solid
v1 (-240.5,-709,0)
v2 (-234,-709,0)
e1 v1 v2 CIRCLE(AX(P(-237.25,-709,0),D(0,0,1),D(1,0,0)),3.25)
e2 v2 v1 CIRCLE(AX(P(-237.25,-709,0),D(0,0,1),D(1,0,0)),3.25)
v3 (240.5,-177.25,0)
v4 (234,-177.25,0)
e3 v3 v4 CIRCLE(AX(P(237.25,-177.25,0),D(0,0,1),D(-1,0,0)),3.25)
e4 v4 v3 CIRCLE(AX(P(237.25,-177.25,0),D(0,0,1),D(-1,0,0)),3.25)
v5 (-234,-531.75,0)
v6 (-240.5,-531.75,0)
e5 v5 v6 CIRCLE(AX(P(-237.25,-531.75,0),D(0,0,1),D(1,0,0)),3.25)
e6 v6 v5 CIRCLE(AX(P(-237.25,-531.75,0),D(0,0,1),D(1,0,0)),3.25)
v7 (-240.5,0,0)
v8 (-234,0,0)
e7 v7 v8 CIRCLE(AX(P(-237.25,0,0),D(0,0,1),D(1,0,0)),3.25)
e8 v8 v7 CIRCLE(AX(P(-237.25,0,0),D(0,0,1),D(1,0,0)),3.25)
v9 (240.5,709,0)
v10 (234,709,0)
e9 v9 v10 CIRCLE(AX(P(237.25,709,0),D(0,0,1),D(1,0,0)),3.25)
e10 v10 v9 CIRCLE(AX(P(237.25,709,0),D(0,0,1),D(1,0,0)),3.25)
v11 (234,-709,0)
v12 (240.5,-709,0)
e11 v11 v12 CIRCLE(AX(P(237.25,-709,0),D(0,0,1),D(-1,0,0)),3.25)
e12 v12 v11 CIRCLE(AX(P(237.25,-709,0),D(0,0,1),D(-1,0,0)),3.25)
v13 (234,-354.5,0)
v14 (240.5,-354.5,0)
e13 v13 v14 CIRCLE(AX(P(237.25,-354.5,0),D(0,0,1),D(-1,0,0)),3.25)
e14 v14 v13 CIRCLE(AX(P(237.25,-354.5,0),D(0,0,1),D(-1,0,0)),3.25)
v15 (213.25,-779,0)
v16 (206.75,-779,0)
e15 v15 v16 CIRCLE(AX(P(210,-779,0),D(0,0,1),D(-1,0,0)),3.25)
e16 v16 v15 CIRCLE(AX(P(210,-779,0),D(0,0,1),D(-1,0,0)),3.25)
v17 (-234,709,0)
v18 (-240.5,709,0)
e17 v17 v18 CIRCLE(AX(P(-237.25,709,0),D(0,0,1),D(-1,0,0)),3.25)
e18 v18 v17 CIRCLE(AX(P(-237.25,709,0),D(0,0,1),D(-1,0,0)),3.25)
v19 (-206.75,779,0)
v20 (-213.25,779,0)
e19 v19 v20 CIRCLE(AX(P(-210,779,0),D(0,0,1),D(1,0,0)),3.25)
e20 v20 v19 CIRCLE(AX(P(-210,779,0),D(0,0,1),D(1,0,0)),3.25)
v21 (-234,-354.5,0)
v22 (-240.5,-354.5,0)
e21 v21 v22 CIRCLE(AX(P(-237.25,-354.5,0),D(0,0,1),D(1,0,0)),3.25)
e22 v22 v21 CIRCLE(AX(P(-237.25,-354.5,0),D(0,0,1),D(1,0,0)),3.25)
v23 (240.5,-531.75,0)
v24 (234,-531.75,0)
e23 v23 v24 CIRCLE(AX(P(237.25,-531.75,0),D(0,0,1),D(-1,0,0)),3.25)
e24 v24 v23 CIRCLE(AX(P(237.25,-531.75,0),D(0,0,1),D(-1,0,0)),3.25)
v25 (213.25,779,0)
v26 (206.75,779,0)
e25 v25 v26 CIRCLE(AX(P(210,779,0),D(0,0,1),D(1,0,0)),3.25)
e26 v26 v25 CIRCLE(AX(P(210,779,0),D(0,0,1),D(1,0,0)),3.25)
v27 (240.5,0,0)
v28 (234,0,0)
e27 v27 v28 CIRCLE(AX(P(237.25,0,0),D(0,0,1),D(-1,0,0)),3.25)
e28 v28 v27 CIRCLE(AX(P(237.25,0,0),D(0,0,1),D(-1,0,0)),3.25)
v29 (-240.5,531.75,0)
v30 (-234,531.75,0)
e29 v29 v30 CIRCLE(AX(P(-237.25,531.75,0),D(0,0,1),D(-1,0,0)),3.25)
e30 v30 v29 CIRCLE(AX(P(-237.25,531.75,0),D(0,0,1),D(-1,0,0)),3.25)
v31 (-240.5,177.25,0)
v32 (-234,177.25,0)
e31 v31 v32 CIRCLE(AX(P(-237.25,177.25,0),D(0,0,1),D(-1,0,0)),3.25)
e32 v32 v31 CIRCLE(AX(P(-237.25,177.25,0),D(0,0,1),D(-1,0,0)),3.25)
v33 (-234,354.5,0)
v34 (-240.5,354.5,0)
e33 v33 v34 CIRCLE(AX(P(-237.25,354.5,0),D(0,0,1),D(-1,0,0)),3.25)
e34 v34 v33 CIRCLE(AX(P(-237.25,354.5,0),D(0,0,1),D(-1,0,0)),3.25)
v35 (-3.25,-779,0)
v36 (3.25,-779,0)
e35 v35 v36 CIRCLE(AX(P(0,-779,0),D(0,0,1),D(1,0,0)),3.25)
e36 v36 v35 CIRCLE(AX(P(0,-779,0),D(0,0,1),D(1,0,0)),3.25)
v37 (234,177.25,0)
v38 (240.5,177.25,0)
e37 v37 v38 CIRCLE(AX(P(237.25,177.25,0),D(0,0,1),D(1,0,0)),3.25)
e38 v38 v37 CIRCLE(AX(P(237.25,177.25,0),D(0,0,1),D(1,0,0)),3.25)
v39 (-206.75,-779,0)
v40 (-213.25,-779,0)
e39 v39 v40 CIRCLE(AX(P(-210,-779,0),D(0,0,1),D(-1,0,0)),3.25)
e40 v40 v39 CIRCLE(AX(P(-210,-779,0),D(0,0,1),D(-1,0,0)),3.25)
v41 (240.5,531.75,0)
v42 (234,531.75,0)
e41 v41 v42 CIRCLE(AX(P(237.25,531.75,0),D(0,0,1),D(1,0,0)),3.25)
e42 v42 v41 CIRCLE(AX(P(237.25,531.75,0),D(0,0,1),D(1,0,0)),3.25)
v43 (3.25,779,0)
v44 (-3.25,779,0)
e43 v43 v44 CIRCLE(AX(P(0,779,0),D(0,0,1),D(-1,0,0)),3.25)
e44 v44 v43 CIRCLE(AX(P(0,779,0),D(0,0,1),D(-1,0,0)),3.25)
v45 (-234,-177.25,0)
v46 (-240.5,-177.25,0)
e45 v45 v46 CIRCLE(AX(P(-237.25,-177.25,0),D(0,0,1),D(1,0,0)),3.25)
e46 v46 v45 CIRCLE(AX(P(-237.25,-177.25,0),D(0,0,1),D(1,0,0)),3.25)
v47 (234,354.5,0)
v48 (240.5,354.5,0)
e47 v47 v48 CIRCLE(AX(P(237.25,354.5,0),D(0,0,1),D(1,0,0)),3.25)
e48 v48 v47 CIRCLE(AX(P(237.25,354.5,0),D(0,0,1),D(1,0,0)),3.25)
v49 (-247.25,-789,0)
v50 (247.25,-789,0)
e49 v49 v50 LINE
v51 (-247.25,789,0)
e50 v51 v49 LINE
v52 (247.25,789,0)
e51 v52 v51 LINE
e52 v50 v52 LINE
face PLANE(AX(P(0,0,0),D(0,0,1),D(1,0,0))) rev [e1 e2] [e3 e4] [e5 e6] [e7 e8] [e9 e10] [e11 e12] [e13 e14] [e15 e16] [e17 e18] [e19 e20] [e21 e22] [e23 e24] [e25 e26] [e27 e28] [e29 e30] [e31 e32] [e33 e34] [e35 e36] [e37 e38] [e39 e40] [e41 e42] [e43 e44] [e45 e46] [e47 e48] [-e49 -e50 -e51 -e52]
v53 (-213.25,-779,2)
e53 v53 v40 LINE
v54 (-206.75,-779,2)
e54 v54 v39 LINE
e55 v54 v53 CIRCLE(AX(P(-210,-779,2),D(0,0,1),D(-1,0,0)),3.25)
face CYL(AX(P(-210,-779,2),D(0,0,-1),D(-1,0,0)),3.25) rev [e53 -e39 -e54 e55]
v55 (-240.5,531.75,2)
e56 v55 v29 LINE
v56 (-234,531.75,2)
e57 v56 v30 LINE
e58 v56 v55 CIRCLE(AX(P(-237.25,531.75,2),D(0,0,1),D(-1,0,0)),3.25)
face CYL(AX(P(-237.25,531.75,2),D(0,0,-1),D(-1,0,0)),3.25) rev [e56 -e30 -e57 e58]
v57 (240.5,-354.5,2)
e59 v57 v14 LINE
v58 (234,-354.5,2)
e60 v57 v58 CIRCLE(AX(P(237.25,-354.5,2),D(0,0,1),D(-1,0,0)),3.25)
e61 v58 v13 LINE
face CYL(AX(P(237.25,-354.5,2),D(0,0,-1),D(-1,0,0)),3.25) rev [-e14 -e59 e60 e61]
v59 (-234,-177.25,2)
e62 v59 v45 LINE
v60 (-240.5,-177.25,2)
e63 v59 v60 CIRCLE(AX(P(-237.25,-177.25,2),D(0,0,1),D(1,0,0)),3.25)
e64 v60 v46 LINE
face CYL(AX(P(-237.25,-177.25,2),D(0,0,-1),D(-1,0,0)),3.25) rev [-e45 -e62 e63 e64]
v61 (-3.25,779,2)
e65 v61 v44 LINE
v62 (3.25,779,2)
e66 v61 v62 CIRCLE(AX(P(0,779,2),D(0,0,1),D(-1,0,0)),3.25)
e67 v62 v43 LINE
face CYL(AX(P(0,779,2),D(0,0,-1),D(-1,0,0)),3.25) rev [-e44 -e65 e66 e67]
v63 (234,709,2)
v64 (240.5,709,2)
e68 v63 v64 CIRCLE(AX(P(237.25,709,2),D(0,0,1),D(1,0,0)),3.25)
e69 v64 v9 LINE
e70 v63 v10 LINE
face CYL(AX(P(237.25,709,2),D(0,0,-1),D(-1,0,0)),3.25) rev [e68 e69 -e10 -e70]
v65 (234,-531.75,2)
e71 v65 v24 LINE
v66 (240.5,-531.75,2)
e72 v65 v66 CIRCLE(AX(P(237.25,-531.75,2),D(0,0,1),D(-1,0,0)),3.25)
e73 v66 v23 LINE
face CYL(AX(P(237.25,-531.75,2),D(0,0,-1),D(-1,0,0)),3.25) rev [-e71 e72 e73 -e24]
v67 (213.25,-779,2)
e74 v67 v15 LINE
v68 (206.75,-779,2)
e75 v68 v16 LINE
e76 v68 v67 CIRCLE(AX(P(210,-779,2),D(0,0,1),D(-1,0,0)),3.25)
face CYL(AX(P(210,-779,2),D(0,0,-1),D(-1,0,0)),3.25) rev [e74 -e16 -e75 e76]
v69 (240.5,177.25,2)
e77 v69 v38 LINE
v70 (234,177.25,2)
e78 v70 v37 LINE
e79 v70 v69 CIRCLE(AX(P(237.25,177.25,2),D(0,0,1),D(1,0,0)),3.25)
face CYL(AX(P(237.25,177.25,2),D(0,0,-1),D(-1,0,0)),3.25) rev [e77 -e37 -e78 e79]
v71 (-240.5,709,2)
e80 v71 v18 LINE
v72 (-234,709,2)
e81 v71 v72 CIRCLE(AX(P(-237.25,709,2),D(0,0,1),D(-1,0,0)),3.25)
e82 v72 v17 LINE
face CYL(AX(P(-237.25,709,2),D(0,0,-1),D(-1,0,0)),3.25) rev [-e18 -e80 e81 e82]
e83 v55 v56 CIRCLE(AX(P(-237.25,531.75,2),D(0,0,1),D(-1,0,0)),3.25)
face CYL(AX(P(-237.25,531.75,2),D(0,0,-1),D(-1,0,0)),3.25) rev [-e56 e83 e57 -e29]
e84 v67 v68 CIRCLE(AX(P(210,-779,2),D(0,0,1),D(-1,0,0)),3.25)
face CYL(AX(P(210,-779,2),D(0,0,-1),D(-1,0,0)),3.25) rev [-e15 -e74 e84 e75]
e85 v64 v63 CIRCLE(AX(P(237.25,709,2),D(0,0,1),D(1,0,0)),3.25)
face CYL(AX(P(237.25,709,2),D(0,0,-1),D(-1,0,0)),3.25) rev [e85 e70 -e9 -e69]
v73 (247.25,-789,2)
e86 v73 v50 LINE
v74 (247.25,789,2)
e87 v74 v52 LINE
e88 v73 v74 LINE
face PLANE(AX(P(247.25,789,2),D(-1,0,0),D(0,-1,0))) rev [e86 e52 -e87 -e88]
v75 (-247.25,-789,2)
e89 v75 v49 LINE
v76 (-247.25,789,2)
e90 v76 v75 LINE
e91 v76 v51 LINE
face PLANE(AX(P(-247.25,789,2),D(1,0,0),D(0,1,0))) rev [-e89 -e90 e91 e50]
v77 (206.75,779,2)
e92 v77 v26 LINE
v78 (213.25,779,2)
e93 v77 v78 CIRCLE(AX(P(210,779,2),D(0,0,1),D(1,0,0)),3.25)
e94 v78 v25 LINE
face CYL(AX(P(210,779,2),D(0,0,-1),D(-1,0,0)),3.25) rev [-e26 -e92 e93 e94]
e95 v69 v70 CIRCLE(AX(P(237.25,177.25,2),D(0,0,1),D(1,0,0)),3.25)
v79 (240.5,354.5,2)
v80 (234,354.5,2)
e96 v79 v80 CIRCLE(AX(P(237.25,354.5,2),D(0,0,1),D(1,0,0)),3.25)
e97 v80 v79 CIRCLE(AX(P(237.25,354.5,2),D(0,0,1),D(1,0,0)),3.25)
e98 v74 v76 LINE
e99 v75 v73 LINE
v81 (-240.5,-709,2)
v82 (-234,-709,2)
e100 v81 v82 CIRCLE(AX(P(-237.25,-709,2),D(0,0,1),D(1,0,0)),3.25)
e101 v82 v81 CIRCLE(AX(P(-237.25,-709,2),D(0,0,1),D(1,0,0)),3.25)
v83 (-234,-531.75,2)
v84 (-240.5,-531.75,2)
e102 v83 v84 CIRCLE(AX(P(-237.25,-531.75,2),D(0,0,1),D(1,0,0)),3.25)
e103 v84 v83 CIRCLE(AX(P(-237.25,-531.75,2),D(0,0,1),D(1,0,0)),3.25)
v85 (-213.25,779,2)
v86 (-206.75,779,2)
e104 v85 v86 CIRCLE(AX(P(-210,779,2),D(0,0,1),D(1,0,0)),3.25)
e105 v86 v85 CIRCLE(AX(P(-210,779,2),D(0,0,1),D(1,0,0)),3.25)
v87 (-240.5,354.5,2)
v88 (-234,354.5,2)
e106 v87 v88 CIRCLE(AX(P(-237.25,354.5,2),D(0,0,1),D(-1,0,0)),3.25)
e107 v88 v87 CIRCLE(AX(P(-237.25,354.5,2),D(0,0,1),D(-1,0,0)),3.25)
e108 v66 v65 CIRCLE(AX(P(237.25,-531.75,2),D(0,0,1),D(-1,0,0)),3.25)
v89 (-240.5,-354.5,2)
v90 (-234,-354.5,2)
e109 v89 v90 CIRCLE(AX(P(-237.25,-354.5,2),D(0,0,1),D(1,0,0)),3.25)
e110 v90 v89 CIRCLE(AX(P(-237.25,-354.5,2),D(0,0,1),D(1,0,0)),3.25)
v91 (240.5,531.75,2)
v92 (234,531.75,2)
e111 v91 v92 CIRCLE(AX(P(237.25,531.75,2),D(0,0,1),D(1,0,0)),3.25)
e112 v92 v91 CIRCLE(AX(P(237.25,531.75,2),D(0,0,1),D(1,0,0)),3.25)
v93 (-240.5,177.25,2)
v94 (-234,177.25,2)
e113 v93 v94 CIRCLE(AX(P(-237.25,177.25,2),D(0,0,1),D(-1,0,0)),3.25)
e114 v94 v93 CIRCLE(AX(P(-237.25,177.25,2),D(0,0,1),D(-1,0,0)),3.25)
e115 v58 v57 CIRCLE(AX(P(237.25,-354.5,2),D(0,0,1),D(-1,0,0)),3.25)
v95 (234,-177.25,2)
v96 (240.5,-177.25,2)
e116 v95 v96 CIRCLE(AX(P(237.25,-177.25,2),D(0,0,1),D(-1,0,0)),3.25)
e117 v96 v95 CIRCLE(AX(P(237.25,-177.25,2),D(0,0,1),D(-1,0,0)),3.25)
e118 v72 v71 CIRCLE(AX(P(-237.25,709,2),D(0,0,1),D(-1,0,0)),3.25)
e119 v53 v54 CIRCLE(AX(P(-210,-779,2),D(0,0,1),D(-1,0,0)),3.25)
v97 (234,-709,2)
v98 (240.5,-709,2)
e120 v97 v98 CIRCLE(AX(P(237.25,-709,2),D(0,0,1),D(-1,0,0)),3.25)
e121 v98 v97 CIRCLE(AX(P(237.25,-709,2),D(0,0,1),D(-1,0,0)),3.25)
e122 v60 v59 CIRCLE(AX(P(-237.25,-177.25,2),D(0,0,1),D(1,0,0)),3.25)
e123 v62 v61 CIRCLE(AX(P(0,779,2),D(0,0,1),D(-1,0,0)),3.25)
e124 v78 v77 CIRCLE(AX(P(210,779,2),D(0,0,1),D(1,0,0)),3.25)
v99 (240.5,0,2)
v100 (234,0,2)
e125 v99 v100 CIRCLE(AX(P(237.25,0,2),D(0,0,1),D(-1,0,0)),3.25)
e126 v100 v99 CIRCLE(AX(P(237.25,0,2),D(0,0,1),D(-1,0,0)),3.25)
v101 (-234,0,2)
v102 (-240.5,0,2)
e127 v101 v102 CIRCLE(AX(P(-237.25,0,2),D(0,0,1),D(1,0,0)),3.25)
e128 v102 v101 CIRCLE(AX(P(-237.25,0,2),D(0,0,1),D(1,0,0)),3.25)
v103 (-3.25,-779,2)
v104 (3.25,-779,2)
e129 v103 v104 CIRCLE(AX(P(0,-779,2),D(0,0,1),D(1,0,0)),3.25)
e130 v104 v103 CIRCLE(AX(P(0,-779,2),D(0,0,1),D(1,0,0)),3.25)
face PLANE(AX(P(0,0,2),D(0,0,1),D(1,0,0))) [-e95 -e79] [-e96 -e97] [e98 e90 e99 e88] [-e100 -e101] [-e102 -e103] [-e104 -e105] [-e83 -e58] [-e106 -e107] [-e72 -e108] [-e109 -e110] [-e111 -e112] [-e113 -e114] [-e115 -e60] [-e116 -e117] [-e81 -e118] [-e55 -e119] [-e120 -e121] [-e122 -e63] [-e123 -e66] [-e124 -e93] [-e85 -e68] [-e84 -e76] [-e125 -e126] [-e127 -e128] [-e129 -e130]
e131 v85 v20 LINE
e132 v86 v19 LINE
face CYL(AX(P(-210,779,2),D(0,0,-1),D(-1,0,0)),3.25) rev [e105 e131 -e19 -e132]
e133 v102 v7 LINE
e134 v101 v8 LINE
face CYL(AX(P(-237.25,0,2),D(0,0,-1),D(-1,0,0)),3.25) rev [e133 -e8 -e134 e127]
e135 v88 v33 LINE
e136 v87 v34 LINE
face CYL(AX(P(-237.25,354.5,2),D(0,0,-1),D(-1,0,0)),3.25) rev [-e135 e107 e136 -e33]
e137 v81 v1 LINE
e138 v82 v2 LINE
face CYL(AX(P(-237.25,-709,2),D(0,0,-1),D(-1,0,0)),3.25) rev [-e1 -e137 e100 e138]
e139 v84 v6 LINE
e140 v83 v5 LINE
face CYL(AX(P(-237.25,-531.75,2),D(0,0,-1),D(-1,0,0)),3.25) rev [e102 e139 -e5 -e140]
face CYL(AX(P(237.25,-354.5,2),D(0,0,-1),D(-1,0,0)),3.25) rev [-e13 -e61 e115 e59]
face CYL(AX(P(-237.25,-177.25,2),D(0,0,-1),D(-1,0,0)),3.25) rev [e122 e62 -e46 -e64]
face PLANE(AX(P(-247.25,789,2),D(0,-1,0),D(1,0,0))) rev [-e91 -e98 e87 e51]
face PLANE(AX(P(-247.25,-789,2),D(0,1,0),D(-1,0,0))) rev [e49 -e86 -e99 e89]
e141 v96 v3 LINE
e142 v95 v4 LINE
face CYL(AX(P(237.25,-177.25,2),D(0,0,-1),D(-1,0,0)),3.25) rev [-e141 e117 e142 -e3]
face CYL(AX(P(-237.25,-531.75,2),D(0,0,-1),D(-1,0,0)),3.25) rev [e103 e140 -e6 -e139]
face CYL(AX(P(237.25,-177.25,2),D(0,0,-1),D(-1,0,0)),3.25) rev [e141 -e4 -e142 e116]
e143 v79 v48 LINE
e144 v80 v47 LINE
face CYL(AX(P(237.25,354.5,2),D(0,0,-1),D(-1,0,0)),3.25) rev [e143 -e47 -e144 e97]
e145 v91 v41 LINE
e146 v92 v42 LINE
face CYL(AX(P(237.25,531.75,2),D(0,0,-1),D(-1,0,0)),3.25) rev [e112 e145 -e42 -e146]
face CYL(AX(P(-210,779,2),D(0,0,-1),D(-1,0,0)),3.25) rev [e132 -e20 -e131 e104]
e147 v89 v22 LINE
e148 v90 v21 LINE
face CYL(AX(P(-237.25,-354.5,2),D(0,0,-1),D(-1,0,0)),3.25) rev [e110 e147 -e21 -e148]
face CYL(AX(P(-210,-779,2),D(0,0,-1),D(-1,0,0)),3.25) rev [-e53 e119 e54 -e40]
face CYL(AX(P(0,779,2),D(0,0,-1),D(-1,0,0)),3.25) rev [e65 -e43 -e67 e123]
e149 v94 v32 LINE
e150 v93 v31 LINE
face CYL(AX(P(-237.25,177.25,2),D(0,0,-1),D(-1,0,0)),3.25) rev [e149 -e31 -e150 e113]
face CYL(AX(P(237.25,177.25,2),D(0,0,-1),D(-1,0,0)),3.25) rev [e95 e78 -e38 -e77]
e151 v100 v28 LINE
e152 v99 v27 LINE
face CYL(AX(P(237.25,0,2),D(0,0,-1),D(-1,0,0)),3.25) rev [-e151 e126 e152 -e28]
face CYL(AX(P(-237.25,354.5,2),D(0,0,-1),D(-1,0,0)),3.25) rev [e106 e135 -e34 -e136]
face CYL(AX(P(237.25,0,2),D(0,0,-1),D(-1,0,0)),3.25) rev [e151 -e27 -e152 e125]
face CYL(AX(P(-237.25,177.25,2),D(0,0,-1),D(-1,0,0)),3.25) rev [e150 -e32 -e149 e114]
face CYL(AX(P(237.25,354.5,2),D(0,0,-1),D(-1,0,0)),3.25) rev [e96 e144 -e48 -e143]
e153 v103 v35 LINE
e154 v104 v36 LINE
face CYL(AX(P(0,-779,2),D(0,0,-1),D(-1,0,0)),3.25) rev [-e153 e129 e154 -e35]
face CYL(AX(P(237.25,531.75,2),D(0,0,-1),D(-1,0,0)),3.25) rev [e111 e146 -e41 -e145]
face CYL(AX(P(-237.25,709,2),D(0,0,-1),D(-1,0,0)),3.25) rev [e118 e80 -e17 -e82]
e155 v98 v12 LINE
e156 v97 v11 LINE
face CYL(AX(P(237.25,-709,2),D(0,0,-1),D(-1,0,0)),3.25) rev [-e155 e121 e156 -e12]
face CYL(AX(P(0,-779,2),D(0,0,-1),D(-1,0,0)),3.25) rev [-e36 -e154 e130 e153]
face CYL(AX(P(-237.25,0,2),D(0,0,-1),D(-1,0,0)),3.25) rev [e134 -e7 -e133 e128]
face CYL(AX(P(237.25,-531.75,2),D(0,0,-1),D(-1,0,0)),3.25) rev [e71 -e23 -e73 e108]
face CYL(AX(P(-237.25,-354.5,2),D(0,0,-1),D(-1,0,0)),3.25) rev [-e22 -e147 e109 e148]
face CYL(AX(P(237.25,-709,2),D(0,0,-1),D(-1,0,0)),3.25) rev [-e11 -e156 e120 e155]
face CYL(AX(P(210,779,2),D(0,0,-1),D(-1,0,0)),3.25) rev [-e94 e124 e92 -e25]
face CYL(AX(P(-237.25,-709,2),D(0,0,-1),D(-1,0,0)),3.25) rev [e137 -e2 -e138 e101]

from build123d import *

# Parameters (mm, degrees)
SKETCH_1_W      = 494.5
SKETCH_1_H      = 1578
SKETCH_1_R      = 3.25
EXTRUDE_1_DEPTH = 2


with BuildPart() as part:
    # 草图1 → 凸台-拉伸1 (new body)
    with BuildSketch(Plane.XY):
        Rectangle(SKETCH_1_W, SKETCH_1_H)
        with Locations((-237.25, 0)):
            Circle(SKETCH_1_R, mode=Mode.SUBTRACT)
        with Locations((-237.25, -177.25)):
            Circle(SKETCH_1_R, mode=Mode.SUBTRACT)
        with Locations((-237.25, -354.5)):
            Circle(SKETCH_1_R, mode=Mode.SUBTRACT)
        with Locations((-237.25, -531.75)):
            Circle(SKETCH_1_R, mode=Mode.SUBTRACT)
        with Locations((-237.25, -709)):
            Circle(SKETCH_1_R, mode=Mode.SUBTRACT)
        with Locations((0, -779)):
            Circle(SKETCH_1_R, mode=Mode.SUBTRACT)
        with Locations(Location((0, 779, 0), (0, 0, 180))):
            Circle(SKETCH_1_R, mode=Mode.SUBTRACT)
        with Locations(Location((-237.25, 709, 0), (0, 0, 180))):
            Circle(SKETCH_1_R, mode=Mode.SUBTRACT)
        with Locations(Location((-237.25, 531.75, 0), (0, 0, 180))):
            Circle(SKETCH_1_R, mode=Mode.SUBTRACT)
        with Locations(Location((-237.25, 354.5, 0), (0, 0, 180))):
            Circle(SKETCH_1_R, mode=Mode.SUBTRACT)
        with Locations(Location((-237.25, 177.25, 0), (0, 0, 180))):
            Circle(SKETCH_1_R, mode=Mode.SUBTRACT)
        with Locations((237.25, 177.25)):
            Circle(SKETCH_1_R, mode=Mode.SUBTRACT)
        with Locations((237.25, 354.5)):
            Circle(SKETCH_1_R, mode=Mode.SUBTRACT)
        with Locations((237.25, 531.75)):
            Circle(SKETCH_1_R, mode=Mode.SUBTRACT)
        with Locations((237.25, 709)):
            Circle(SKETCH_1_R, mode=Mode.SUBTRACT)
        with Locations(Location((237.25, -709, 0), (0, 0, 180))):
            Circle(SKETCH_1_R, mode=Mode.SUBTRACT)
        with Locations(Location((237.25, -531.75, 0), (0, 0, 180))):
            Circle(SKETCH_1_R, mode=Mode.SUBTRACT)
        with Locations(Location((237.25, -354.5, 0), (0, 0, 180))):
            Circle(SKETCH_1_R, mode=Mode.SUBTRACT)
        with Locations(Location((237.25, -177.25, 0), (0, 0, 180))):
            Circle(SKETCH_1_R, mode=Mode.SUBTRACT)
        with Locations(Location((237.25, 0, 0), (0, 0, 180))):
            Circle(SKETCH_1_R, mode=Mode.SUBTRACT)
        with Locations((-210, 779)):
            Circle(SKETCH_1_R, mode=Mode.SUBTRACT)
        with Locations((210, 779)):
            Circle(SKETCH_1_R, mode=Mode.SUBTRACT)
        with Locations(Location((210, -779, 0), (0, 0, 180))):
            Circle(SKETCH_1_R, mode=Mode.SUBTRACT)
        with Locations(Location((-210, -779, 0), (0, 0, 180))):
            Circle(SKETCH_1_R, mode=Mode.SUBTRACT)
    extrude(amount=EXTRUDE_1_DEPTH)


solid = part.part
